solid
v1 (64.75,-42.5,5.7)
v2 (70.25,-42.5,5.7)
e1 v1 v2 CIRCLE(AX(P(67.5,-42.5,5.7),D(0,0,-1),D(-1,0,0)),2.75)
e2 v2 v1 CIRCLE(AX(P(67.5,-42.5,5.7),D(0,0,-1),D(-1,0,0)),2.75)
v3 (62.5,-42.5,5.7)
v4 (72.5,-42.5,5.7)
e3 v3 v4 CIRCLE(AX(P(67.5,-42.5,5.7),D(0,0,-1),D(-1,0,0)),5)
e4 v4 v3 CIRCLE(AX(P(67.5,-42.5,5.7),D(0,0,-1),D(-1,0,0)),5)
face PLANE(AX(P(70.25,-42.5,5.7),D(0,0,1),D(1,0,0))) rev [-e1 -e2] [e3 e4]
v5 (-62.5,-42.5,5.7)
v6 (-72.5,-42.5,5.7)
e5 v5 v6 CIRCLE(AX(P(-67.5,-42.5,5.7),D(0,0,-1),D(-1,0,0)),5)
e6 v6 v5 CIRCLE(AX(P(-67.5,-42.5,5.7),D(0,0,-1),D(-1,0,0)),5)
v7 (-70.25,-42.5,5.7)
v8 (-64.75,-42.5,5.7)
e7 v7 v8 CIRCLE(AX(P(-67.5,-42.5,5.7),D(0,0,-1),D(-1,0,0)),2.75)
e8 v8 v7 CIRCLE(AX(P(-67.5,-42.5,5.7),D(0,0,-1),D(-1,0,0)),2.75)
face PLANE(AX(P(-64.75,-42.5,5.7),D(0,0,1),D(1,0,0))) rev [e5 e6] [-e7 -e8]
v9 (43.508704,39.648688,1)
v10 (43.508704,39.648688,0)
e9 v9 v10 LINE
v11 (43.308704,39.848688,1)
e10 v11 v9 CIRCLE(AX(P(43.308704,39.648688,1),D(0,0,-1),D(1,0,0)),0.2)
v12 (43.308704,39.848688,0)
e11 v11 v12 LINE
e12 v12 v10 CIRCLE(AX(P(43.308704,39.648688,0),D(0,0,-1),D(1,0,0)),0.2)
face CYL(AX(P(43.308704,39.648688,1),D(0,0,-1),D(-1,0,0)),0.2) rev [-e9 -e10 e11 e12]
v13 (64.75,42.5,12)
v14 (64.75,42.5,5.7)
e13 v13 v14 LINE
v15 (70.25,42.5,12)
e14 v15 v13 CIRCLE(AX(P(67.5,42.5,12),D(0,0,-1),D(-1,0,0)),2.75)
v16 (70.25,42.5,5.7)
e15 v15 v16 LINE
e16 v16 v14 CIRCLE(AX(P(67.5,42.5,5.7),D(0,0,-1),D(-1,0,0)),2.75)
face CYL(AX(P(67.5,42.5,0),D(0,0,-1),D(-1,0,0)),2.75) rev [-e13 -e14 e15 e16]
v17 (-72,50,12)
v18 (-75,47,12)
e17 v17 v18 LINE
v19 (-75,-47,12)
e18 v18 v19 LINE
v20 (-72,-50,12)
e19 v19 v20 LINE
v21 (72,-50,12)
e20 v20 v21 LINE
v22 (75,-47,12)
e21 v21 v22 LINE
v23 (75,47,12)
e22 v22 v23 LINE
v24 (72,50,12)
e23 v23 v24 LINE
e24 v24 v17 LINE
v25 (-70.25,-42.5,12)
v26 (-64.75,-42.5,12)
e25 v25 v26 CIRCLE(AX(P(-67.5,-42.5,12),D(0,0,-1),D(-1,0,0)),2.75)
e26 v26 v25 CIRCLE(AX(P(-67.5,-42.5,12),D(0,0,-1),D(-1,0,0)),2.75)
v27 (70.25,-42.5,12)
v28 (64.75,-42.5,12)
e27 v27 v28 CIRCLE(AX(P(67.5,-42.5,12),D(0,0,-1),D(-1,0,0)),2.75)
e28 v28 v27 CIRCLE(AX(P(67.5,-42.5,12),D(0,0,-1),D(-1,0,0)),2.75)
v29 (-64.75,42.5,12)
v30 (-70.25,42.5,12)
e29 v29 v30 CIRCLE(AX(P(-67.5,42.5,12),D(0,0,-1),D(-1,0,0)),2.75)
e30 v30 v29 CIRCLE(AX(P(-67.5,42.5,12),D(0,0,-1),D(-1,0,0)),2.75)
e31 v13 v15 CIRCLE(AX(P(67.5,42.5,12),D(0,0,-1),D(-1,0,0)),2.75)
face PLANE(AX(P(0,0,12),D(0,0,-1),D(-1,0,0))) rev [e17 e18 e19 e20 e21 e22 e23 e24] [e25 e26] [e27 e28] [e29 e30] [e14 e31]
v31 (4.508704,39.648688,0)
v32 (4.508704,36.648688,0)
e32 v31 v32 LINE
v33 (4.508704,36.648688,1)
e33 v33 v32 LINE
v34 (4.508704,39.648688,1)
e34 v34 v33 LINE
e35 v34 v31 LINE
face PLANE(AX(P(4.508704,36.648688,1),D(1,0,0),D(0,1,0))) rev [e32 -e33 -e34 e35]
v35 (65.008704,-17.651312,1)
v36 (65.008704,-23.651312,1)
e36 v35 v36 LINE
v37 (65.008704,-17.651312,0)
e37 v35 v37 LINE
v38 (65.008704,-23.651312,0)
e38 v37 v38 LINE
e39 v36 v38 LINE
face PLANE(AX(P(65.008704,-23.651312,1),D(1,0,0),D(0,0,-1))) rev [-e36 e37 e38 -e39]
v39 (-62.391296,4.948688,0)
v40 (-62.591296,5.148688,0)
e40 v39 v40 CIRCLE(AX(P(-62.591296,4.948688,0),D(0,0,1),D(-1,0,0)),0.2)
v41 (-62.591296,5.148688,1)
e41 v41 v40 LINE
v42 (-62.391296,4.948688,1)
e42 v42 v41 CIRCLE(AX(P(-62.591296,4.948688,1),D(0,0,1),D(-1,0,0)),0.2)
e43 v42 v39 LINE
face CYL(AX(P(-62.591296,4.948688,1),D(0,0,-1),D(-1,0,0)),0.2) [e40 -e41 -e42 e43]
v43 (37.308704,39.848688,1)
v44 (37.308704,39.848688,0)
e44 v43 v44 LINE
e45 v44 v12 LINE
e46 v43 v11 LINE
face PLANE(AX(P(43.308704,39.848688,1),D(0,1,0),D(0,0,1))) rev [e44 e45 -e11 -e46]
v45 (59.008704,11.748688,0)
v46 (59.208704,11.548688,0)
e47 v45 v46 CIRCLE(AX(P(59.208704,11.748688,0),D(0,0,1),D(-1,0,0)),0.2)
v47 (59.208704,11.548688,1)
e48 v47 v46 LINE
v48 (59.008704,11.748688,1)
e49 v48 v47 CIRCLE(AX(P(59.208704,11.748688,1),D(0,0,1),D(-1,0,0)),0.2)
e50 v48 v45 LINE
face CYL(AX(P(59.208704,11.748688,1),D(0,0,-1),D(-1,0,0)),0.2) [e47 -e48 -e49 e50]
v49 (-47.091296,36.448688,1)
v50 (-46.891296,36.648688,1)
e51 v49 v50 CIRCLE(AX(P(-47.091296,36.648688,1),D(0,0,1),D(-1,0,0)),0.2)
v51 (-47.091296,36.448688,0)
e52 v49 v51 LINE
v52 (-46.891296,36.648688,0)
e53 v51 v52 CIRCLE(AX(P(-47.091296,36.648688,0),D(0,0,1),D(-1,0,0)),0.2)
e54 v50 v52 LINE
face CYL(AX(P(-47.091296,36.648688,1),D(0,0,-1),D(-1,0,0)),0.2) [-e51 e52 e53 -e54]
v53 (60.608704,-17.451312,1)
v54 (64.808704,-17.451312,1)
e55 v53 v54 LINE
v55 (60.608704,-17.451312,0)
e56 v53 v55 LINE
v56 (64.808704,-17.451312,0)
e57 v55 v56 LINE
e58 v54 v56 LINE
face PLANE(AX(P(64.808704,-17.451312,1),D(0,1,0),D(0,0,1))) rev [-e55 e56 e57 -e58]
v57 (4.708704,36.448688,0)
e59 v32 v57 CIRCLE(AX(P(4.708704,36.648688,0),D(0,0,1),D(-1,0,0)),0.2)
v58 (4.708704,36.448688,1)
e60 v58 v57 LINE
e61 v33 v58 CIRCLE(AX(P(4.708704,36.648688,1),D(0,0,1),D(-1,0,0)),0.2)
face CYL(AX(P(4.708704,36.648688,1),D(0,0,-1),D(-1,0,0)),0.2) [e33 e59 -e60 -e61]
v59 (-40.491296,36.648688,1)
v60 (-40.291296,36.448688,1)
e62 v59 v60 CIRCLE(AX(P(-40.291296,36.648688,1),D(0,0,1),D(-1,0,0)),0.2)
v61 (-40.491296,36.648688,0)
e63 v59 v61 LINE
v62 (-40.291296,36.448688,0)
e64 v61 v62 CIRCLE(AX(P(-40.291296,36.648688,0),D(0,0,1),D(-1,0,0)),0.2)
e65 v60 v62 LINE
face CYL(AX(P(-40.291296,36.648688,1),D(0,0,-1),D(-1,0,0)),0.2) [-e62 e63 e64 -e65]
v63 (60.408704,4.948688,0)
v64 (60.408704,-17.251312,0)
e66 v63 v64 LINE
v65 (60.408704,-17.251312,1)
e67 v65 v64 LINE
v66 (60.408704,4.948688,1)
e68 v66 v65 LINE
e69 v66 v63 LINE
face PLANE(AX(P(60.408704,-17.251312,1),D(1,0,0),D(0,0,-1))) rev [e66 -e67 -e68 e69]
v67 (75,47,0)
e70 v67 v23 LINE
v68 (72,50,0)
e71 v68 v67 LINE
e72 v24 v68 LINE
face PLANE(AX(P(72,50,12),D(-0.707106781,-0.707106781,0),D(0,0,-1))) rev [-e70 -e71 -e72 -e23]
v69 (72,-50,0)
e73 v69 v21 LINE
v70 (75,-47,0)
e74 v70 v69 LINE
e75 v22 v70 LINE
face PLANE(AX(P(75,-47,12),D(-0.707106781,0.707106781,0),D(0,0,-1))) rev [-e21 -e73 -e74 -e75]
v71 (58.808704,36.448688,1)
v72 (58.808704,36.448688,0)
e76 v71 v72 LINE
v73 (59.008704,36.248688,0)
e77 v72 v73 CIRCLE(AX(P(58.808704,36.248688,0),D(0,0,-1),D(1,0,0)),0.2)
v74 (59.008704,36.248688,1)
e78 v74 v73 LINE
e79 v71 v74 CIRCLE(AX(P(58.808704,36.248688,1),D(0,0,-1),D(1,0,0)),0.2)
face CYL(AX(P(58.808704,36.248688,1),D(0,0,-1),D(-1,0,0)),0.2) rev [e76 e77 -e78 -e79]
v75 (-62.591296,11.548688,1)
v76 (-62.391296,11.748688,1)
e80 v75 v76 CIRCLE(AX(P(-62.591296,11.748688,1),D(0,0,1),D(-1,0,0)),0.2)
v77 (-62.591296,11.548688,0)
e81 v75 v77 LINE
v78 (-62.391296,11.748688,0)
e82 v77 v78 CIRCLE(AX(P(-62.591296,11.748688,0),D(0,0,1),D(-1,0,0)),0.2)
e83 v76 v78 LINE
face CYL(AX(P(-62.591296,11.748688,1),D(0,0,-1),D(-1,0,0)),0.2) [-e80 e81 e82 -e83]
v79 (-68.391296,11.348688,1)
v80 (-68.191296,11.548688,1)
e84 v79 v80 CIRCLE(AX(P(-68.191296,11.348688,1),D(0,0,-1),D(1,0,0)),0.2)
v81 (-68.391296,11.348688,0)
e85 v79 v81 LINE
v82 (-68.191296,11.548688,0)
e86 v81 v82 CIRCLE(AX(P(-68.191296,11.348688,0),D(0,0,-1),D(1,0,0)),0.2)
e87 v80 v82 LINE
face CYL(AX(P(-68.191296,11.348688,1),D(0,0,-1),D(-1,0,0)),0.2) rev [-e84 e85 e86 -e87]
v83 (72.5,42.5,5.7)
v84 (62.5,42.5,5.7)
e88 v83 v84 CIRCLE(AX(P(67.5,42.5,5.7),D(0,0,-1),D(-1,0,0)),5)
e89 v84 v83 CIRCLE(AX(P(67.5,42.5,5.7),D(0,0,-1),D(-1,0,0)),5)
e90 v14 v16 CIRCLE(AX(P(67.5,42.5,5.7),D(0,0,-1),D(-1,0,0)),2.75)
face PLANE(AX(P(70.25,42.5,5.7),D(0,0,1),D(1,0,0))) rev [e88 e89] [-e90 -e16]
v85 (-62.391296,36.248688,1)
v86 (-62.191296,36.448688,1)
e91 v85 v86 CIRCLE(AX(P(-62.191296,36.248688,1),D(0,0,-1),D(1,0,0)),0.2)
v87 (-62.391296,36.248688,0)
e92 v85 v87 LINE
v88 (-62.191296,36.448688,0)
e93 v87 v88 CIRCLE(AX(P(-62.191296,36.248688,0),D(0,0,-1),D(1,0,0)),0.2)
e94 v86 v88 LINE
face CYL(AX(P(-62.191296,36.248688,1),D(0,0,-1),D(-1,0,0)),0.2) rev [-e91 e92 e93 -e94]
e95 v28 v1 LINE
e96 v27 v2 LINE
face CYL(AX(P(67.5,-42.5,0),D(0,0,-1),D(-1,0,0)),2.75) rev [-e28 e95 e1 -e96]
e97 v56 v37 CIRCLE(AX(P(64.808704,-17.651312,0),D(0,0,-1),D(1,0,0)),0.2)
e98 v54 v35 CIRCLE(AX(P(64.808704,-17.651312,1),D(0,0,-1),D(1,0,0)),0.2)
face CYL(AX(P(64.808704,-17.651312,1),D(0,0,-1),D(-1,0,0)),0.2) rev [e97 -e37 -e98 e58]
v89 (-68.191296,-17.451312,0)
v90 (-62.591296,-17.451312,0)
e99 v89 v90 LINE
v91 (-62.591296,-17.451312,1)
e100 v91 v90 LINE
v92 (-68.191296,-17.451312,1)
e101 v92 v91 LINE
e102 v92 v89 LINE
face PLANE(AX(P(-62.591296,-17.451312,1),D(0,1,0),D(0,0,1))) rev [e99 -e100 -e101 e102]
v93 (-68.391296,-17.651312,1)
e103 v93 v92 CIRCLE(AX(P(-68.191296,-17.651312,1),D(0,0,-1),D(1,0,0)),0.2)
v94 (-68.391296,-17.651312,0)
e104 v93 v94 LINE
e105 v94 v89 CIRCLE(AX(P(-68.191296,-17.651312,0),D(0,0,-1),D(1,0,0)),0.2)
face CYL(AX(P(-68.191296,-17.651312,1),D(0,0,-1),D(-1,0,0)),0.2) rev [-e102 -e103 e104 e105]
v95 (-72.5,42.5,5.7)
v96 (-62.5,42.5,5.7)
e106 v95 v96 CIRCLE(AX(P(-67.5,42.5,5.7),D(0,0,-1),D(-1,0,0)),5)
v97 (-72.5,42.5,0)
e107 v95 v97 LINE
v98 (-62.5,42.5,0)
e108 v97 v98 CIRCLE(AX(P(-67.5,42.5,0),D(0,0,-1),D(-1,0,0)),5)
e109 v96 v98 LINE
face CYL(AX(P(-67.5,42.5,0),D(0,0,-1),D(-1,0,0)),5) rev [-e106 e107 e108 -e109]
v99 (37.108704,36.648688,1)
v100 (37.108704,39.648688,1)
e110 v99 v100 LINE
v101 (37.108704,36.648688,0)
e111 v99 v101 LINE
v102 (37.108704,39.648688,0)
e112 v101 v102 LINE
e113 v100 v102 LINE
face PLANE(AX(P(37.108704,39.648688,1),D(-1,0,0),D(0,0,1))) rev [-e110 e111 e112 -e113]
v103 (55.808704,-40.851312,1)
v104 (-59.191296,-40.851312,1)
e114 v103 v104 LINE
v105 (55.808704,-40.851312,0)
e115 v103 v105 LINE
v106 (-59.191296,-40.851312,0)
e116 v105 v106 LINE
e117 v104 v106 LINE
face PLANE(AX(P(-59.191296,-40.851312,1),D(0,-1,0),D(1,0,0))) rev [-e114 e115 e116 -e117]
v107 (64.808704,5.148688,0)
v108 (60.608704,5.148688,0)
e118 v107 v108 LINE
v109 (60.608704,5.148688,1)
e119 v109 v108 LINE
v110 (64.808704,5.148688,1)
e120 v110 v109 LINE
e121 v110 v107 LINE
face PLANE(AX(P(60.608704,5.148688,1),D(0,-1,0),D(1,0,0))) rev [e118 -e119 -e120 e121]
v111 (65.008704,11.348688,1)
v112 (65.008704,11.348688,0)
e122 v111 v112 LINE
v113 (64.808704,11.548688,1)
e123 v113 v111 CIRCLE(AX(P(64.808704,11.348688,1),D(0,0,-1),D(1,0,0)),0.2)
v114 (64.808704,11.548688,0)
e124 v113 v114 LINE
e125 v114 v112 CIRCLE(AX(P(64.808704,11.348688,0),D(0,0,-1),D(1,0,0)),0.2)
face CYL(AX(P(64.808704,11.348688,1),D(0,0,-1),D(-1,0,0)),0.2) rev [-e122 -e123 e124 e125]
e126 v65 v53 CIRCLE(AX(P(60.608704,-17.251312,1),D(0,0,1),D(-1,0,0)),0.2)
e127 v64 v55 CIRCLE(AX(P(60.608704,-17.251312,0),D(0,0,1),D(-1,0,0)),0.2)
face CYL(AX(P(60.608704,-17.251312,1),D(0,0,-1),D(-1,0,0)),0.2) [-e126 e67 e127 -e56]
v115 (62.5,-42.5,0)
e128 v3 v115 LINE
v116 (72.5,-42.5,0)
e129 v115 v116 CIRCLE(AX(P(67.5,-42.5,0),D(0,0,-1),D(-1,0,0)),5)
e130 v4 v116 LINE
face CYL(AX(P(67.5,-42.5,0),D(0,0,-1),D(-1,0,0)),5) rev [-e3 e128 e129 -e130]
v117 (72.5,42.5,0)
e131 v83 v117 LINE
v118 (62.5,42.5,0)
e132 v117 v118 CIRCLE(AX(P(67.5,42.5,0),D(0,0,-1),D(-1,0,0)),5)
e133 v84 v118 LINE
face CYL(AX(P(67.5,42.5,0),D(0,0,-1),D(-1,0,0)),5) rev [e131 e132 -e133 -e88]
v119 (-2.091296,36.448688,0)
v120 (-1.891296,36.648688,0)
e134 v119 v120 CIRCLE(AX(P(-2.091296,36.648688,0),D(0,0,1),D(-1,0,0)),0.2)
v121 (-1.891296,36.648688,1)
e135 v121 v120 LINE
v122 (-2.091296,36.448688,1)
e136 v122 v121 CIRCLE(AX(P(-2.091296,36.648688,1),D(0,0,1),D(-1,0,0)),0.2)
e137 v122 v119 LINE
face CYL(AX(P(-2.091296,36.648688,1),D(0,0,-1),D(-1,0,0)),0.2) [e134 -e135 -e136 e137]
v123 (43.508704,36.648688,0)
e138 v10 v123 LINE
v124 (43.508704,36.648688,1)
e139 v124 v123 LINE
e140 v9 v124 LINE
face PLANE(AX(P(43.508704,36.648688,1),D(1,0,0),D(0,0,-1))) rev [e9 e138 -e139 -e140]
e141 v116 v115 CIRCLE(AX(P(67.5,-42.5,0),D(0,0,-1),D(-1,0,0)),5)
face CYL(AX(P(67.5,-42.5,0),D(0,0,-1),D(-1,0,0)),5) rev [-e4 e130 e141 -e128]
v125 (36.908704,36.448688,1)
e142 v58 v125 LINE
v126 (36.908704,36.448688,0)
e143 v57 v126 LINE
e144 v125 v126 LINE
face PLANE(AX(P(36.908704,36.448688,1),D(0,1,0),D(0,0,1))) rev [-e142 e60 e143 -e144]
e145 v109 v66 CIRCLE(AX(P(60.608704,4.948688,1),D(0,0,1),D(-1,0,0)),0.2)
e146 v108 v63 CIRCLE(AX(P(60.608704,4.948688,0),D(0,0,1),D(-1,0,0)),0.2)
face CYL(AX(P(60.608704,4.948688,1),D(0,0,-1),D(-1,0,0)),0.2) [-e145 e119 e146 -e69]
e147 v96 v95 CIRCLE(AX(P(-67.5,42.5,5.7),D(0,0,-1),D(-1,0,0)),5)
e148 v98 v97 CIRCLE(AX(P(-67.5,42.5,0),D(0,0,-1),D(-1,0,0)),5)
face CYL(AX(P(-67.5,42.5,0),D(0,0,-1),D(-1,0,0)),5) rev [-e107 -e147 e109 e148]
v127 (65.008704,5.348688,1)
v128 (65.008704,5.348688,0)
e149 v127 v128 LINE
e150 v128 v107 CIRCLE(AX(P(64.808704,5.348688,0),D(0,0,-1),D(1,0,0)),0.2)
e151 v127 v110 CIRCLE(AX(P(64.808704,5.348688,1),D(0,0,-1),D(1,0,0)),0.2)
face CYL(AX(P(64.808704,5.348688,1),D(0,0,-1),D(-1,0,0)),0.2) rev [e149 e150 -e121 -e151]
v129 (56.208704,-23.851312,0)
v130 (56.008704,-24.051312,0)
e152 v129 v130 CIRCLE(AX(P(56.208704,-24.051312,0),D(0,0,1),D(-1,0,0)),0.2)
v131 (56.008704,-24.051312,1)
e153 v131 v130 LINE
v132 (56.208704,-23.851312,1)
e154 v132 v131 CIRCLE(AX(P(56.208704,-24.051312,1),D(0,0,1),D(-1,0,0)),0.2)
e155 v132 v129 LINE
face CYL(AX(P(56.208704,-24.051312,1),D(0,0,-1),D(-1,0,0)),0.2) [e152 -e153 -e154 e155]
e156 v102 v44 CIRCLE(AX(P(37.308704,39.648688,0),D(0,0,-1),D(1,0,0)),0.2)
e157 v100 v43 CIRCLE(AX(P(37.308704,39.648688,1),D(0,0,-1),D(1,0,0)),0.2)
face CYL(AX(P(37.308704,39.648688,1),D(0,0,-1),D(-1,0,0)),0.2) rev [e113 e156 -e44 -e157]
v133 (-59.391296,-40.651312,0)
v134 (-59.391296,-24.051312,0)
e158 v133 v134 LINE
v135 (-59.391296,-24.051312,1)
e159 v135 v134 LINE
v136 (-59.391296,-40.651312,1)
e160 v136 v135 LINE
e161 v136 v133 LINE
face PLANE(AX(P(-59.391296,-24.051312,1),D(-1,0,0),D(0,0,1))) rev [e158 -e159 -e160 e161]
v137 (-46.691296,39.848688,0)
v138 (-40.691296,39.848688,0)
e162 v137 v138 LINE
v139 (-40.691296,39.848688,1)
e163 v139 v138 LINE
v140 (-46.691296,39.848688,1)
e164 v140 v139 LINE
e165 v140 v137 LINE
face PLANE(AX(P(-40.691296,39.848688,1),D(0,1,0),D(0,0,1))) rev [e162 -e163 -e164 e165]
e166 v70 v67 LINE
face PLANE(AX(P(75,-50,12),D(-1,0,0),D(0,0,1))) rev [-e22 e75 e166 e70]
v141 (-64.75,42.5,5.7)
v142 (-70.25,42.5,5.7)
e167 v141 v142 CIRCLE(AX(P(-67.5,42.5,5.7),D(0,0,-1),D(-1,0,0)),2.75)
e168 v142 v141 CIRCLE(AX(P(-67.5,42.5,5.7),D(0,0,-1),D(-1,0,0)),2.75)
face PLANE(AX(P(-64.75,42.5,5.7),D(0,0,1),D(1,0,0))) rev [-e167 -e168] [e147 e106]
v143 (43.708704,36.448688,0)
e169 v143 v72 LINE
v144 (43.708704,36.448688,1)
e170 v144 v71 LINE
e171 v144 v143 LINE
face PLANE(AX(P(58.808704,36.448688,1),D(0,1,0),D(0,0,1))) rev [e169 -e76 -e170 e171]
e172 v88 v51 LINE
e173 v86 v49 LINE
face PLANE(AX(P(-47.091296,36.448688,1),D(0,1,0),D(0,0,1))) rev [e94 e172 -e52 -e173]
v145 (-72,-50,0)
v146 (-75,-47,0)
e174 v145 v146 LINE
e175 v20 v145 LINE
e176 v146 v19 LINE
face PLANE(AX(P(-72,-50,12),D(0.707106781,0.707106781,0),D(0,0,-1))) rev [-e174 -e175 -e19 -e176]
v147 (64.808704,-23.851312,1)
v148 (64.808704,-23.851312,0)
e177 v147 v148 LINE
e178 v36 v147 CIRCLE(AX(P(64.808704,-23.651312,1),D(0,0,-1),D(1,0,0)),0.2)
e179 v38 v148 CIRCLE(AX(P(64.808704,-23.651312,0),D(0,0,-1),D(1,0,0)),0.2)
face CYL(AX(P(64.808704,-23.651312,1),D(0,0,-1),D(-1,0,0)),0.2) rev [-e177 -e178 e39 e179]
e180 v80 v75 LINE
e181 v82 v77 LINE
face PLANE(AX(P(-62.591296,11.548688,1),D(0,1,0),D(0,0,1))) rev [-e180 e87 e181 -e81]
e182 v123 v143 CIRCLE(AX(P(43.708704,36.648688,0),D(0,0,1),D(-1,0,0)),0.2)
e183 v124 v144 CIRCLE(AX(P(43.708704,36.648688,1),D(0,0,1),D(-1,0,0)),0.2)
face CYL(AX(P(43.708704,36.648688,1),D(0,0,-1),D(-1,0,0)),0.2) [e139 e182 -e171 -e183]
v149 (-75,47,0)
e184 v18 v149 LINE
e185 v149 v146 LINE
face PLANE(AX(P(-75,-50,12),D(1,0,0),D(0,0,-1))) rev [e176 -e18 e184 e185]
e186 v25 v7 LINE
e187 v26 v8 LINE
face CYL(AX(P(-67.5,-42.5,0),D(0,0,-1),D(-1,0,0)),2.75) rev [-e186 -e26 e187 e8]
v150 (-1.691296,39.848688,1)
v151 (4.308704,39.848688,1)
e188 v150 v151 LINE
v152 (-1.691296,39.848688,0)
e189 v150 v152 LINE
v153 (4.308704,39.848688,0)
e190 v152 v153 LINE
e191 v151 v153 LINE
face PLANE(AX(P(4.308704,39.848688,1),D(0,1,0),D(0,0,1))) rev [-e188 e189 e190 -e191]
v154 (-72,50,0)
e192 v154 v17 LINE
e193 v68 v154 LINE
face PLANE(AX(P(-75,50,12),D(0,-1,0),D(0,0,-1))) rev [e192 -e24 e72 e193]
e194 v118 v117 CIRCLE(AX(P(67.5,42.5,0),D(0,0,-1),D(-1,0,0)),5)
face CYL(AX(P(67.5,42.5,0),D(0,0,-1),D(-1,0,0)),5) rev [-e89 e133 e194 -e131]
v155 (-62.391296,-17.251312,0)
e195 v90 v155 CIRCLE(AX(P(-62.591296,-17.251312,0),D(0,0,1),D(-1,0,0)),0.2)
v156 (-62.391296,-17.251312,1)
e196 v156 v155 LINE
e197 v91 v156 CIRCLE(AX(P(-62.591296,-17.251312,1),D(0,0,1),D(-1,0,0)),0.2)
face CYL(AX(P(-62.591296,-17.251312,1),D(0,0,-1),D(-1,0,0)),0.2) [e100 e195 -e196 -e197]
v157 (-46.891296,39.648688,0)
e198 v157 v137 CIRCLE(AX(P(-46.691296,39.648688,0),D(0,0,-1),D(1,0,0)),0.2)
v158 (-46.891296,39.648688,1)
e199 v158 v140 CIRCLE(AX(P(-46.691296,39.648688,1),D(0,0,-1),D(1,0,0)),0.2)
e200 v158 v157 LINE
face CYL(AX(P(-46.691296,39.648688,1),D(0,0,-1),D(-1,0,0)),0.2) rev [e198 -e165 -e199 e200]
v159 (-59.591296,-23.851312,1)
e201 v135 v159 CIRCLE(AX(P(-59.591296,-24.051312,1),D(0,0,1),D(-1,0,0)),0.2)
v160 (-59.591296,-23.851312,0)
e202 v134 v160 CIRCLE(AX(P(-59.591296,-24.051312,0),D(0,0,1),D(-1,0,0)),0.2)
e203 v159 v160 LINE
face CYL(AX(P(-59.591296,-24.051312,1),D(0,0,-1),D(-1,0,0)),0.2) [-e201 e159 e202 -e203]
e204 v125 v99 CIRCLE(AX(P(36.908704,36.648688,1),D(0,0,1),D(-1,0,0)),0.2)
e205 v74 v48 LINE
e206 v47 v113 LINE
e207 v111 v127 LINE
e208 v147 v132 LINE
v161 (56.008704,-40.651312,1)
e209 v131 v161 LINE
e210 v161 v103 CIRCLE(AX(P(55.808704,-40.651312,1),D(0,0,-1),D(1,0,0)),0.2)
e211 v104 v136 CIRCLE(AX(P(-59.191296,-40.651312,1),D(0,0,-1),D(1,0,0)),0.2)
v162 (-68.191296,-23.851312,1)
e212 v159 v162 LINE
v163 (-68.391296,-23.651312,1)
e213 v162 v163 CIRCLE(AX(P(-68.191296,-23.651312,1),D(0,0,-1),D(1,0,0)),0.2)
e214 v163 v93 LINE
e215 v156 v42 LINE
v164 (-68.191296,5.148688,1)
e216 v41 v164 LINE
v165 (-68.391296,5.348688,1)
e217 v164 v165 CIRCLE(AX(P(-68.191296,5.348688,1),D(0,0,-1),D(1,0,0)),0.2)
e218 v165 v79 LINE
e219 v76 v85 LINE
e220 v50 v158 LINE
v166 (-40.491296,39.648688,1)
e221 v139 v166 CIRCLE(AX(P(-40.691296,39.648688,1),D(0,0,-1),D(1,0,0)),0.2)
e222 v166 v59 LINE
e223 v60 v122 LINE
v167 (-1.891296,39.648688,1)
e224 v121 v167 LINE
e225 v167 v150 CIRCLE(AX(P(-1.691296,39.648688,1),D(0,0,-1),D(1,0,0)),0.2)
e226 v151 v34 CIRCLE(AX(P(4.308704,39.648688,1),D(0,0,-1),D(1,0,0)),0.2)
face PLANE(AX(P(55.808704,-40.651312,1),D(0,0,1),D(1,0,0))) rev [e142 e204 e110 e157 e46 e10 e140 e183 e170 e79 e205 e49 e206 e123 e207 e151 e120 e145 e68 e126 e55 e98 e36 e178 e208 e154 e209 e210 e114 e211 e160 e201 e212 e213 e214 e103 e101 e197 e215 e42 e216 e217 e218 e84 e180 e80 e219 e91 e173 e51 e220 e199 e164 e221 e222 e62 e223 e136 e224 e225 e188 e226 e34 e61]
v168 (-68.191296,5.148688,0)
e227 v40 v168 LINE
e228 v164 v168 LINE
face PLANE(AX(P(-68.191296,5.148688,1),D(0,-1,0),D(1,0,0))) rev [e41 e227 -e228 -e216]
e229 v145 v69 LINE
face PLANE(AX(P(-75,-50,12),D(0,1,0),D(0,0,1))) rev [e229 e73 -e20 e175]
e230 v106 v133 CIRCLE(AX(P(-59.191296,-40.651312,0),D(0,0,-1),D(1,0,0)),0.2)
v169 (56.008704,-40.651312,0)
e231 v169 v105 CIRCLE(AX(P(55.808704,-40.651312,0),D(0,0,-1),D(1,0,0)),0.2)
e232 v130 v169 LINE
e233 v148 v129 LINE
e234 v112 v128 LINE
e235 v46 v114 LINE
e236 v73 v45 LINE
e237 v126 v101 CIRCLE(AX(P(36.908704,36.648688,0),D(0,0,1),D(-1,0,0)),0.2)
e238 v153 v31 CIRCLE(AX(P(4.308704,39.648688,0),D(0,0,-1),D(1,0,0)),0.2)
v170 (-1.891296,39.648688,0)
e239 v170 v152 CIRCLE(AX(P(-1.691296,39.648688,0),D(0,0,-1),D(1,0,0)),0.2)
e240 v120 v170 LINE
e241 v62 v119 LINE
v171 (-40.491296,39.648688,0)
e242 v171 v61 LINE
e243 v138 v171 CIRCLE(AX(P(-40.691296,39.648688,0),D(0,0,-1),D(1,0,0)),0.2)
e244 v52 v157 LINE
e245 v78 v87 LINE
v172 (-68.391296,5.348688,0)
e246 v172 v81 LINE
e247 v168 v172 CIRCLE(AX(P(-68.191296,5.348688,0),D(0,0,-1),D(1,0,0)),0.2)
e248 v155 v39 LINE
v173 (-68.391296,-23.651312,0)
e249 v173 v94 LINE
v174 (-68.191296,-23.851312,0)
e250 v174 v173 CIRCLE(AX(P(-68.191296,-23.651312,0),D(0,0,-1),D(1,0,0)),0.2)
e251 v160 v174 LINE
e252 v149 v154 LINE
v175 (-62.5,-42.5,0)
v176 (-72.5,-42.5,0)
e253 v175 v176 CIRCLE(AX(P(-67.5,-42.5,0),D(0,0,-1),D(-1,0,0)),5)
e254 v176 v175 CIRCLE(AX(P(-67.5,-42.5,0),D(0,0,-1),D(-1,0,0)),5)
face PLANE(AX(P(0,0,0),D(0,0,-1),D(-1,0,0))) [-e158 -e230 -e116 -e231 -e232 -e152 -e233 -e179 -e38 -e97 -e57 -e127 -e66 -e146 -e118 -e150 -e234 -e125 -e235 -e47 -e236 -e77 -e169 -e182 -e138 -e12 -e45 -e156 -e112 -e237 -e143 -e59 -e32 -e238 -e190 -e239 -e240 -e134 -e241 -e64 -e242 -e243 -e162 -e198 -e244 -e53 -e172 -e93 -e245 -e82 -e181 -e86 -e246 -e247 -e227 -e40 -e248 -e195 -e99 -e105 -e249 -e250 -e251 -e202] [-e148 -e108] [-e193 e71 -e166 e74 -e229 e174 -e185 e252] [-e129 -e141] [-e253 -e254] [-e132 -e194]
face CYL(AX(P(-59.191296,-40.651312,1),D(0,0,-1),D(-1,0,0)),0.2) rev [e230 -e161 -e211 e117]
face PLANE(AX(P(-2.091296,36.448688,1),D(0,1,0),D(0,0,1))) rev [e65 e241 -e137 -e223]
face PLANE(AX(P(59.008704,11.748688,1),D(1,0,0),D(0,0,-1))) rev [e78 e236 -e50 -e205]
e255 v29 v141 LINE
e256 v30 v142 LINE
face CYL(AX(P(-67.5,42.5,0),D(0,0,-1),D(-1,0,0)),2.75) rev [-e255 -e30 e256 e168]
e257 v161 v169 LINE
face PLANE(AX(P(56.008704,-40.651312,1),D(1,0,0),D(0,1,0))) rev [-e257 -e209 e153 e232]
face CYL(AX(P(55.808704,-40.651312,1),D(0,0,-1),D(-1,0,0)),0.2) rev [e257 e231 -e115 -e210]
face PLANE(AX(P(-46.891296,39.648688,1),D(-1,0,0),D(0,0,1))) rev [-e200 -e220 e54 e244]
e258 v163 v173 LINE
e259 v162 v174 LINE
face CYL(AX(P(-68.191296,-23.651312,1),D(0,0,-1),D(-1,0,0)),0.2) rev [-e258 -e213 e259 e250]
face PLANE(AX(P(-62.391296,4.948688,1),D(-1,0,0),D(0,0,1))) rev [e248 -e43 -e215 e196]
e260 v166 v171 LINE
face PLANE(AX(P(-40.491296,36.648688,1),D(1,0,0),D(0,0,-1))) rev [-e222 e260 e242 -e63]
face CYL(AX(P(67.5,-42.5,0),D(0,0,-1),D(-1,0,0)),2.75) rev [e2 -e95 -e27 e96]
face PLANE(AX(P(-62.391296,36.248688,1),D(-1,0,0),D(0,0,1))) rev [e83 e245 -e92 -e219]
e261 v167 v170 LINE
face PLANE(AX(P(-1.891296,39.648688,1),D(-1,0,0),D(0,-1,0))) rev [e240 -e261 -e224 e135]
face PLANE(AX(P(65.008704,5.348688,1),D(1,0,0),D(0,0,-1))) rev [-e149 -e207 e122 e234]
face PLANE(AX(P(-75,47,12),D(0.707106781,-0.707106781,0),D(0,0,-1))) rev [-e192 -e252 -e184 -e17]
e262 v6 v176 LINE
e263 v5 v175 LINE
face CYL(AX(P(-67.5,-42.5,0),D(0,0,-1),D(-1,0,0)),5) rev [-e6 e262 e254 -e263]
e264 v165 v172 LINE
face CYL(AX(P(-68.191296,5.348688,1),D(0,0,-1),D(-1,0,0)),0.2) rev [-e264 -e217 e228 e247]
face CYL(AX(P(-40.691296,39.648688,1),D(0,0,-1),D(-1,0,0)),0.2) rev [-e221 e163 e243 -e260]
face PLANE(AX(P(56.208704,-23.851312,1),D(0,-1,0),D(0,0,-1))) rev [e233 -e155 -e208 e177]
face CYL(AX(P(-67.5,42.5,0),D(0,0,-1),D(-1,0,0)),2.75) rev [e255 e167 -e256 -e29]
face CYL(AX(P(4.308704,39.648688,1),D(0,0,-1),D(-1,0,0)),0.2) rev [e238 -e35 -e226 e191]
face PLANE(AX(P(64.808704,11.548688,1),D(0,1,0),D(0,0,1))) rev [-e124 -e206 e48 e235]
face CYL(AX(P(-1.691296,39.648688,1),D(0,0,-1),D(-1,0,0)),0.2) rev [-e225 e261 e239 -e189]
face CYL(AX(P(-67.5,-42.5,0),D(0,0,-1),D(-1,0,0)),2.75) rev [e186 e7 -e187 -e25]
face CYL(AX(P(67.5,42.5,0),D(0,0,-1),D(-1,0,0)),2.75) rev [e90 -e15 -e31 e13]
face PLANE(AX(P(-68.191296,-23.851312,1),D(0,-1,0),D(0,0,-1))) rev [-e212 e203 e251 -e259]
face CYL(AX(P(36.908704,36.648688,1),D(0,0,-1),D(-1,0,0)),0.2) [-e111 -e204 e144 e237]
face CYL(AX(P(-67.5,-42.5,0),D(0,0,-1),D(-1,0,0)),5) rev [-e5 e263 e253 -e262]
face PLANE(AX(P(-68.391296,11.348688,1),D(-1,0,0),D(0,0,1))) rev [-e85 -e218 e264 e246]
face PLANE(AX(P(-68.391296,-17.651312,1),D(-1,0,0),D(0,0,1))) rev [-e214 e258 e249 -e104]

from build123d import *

# Parameters (mm, degrees)
SKETCH1_W                                         = 150
SKETCH1_H                                         = 100
BOSS_EXTRUDE1_DEPTH                               = 12
CUT_EXTRUDE3_DEPTH                                = 1
CHAMFER1_SIZE                                     = 3
HOLE_SIZE_BASED_SOCKET_HEAD_CAP_SCREW_D           = 5.5
HOLE_SIZE_BASED_SOCKET_HEAD_CAP_SCREW_CBORE_D     = 10
HOLE_SIZE_BASED_SOCKET_HEAD_CAP_SCREW_CBORE_DEPTH = 5.7


with BuildPart() as part:
    # Sketch1 → Boss-Extrude1 (new body)
    with BuildSketch(Plane.XY):
        Rectangle(SKETCH1_W, SKETCH1_H)
    extrude(amount=BOSS_EXTRUDE1_DEPTH)

    # Sketch5 → Cut-Extrude3 (cut)
    with BuildSketch(Plane(origin=(0, 0, 0), x_dir=(-1, 0, 0), z_dir=(0, 0, -1))):
        with BuildLine():
            Line((-56.0087044, -40.651312408), (-56.0087044, -24.051312408))
            ThreePointArc((-56.0087044, -24.051312408), (-56.067283044, -23.909891052), (-56.2087044, -23.851312408))
            Line((-56.2087044, -23.851312408), (-64.8087044, -23.851312408))
            ThreePointArc((-64.8087044, -23.851312408), (-64.950125756, -23.792733764), (-65.0087044, -23.651312408))
            Line((-65.0087044, -23.651312408), (-65.0087044, -17.651312408))
            ThreePointArc((-65.0087044, -17.651312408), (-64.950125756, -17.509891052), (-64.8087044, -17.451312408))
            Line((-64.8087044, -17.451312408), (-60.6087044, -17.451312408))
            ThreePointArc((-60.6087044, -17.451312408), (-60.467283044, -17.392733764), (-60.4087044, -17.251312408))
            Line((-60.4087044, -17.251312408), (-60.4087044, 4.948687592))
            ThreePointArc((-60.4087044, 4.948687592), (-60.467283044, 5.090108948), (-60.6087044, 5.148687592))
            Line((-60.6087044, 5.148687592), (-64.8087044, 5.148687592))
            ThreePointArc((-64.8087044, 5.148687592), (-64.950125756, 5.207266236), (-65.0087044, 5.348687592))
            Line((-65.0087044, 5.348687592), (-65.0087044, 11.348687592))
            ThreePointArc((-65.0087044, 11.348687592), (-64.950125756, 11.490108948), (-64.8087044, 11.548687592))
            Line((-64.8087044, 11.548687592), (-59.2087044, 11.548687592))
            ThreePointArc((-59.2087044, 11.548687592), (-59.067283044, 11.607266236), (-59.0087044, 11.748687592))
            Line((-59.0087044, 11.748687592), (-59.0087044, 36.248687592))
            ThreePointArc((-59.0087044, 36.248687592), (-58.950125756, 36.390108948), (-58.8087044, 36.448687592))
            Line((-58.8087044, 36.448687592), (-43.7087044, 36.448687592))
            ThreePointArc((-43.7087044, 36.448687592), (-43.567283044, 36.507266236), (-43.5087044, 36.648687592))
            Line((-43.5087044, 36.648687592), (-43.5087044, 39.648687592))
            ThreePointArc((-43.5087044, 39.648687592), (-43.450125756, 39.790108948), (-43.3087044, 39.848687592))
            Line((-43.3087044, 39.848687592), (-37.3087044, 39.848687592))
            ThreePointArc((-37.3087044, 39.848687592), (-37.167283044, 39.790108948), (-37.1087044, 39.648687592))
            Line((-37.1087044, 39.648687592), (-37.1087044, 36.648687592))
            ThreePointArc((-37.1087044, 36.648687592), (-37.050125756, 36.507266236), (-36.9087044, 36.448687592))
            Line((-36.9087044, 36.448687592), (-4.7087044, 36.448687592))
            ThreePointArc((-4.7087044, 36.448687592), (-4.567283044, 36.507266236), (-4.5087044, 36.648687592))
            Line((-4.5087044, 36.648687592), (-4.5087044, 39.648687592))
            ThreePointArc((-4.5087044, 39.648687592), (-4.450125756, 39.790108948), (-4.3087044, 39.848687592))
            Line((-4.3087044, 39.848687592), (1.6912956, 39.848687592))
            ThreePointArc((1.6912956, 39.848687592), (1.832716956, 39.790108948), (1.8912956, 39.648687592))
            Line((1.8912956, 39.648687592), (1.8912956, 36.648687592))
            ThreePointArc((1.8912956, 36.648687592), (1.949874244, 36.507266236), (2.0912956, 36.448687592))
            Line((2.0912956, 36.448687592), (40.2912956, 36.448687592))
            ThreePointArc((40.2912956, 36.448687592), (40.432716956, 36.507266236), (40.4912956, 36.648687592))
            Line((40.4912956, 36.648687592), (40.4912956, 39.648687592))
            ThreePointArc((40.4912956, 39.648687592), (40.549874244, 39.790108948), (40.6912956, 39.848687592))
            Line((40.6912956, 39.848687592), (46.6912956, 39.848687592))
            ThreePointArc((46.6912956, 39.848687592), (46.832716956, 39.790108948), (46.8912956, 39.648687592))
            Line((46.8912956, 39.648687592), (46.8912956, 36.648687592))
            ThreePointArc((46.8912956, 36.648687592), (46.949874244, 36.507266236), (47.0912956, 36.448687592))
            Line((47.0912956, 36.448687592), (62.1912956, 36.448687592))
            ThreePointArc((62.1912956, 36.448687592), (62.332716956, 36.390108948), (62.3912956, 36.248687592))
            Line((62.3912956, 36.248687592), (62.3912956, 11.748687592))
            ThreePointArc((62.3912956, 11.748687592), (62.449874244, 11.607266236), (62.5912956, 11.548687592))
            Line((62.5912956, 11.548687592), (68.1912956, 11.548687592))
            ThreePointArc((68.1912956, 11.548687592), (68.332716956, 11.490108948), (68.3912956, 11.348687592))
            Line((68.3912956, 11.348687592), (68.3912956, 5.348687592))
            ThreePointArc((68.3912956, 5.348687592), (68.332716956, 5.207266236), (68.1912956, 5.148687592))
            Line((68.1912956, 5.148687592), (62.5912956, 5.148687592))
            ThreePointArc((62.5912956, 5.148687592), (62.449874244, 5.090108948), (62.3912956, 4.948687592))
            Line((62.3912956, 4.948687592), (62.3912956, -17.251312408))
            ThreePointArc((62.3912956, -17.251312408), (62.449874244, -17.392733764), (62.5912956, -17.451312408))
            Line((62.5912956, -17.451312408), (68.1912956, -17.451312408))
            ThreePointArc((68.1912956, -17.451312408), (68.332716956, -17.509891052), (68.3912956, -17.651312408))
            Line((68.3912956, -17.651312408), (68.3912956, -23.651312408))
            ThreePointArc((68.3912956, -23.651312408), (68.332716956, -23.792733764), (68.1912956, -23.851312408))
            Line((68.1912956, -23.851312408), (59.5912956, -23.851312408))
            ThreePointArc((59.5912956, -23.851312408), (59.449874244, -23.909891052), (59.3912956, -24.051312408))
            Line((59.3912956, -24.051312408), (59.3912956, -40.651312408))
            ThreePointArc((59.3912956, -40.651312408), (59.332716956, -40.792733764), (59.1912956, -40.851312408))
            Line((59.1912956, -40.851312408), (-55.8087044, -40.851312408))
            ThreePointArc((-55.8087044, -40.851312408), (-55.950125756, -40.792733764), (-56.0087044, -40.651312408))
        make_face()
    extrude(amount=-CUT_EXTRUDE3_DEPTH, mode=Mode.SUBTRACT)

    # Chamfer1
    chamfer1_edges = [part.edges().sort_by_distance(p)[0] for p in [
        (75, -50, 6),
        (-75, -50, 6),
        (-75, 50, 6),
        (75, 50, 6),
    ]]
    chamfer(chamfer1_edges, length=CHAMFER1_SIZE)

    # Hole Size (%based) Socket Head Cap Screw Type1 (through all)
    with Locations(Plane(origin=(0, 0, 0), x_dir=(-1, 0, 0), z_dir=(0, 0, -1))):
        with Locations((-67.5, 42.5), (67.5, 42.5), (67.5, -42.5), (-67.5, -42.5)):
            CounterBoreHole(HOLE_SIZE_BASED_SOCKET_HEAD_CAP_SCREW_D / 2, HOLE_SIZE_BASED_SOCKET_HEAD_CAP_SCREW_CBORE_D / 2, HOLE_SIZE_BASED_SOCKET_HEAD_CAP_SCREW_CBORE_DEPTH)


solid = part.part
